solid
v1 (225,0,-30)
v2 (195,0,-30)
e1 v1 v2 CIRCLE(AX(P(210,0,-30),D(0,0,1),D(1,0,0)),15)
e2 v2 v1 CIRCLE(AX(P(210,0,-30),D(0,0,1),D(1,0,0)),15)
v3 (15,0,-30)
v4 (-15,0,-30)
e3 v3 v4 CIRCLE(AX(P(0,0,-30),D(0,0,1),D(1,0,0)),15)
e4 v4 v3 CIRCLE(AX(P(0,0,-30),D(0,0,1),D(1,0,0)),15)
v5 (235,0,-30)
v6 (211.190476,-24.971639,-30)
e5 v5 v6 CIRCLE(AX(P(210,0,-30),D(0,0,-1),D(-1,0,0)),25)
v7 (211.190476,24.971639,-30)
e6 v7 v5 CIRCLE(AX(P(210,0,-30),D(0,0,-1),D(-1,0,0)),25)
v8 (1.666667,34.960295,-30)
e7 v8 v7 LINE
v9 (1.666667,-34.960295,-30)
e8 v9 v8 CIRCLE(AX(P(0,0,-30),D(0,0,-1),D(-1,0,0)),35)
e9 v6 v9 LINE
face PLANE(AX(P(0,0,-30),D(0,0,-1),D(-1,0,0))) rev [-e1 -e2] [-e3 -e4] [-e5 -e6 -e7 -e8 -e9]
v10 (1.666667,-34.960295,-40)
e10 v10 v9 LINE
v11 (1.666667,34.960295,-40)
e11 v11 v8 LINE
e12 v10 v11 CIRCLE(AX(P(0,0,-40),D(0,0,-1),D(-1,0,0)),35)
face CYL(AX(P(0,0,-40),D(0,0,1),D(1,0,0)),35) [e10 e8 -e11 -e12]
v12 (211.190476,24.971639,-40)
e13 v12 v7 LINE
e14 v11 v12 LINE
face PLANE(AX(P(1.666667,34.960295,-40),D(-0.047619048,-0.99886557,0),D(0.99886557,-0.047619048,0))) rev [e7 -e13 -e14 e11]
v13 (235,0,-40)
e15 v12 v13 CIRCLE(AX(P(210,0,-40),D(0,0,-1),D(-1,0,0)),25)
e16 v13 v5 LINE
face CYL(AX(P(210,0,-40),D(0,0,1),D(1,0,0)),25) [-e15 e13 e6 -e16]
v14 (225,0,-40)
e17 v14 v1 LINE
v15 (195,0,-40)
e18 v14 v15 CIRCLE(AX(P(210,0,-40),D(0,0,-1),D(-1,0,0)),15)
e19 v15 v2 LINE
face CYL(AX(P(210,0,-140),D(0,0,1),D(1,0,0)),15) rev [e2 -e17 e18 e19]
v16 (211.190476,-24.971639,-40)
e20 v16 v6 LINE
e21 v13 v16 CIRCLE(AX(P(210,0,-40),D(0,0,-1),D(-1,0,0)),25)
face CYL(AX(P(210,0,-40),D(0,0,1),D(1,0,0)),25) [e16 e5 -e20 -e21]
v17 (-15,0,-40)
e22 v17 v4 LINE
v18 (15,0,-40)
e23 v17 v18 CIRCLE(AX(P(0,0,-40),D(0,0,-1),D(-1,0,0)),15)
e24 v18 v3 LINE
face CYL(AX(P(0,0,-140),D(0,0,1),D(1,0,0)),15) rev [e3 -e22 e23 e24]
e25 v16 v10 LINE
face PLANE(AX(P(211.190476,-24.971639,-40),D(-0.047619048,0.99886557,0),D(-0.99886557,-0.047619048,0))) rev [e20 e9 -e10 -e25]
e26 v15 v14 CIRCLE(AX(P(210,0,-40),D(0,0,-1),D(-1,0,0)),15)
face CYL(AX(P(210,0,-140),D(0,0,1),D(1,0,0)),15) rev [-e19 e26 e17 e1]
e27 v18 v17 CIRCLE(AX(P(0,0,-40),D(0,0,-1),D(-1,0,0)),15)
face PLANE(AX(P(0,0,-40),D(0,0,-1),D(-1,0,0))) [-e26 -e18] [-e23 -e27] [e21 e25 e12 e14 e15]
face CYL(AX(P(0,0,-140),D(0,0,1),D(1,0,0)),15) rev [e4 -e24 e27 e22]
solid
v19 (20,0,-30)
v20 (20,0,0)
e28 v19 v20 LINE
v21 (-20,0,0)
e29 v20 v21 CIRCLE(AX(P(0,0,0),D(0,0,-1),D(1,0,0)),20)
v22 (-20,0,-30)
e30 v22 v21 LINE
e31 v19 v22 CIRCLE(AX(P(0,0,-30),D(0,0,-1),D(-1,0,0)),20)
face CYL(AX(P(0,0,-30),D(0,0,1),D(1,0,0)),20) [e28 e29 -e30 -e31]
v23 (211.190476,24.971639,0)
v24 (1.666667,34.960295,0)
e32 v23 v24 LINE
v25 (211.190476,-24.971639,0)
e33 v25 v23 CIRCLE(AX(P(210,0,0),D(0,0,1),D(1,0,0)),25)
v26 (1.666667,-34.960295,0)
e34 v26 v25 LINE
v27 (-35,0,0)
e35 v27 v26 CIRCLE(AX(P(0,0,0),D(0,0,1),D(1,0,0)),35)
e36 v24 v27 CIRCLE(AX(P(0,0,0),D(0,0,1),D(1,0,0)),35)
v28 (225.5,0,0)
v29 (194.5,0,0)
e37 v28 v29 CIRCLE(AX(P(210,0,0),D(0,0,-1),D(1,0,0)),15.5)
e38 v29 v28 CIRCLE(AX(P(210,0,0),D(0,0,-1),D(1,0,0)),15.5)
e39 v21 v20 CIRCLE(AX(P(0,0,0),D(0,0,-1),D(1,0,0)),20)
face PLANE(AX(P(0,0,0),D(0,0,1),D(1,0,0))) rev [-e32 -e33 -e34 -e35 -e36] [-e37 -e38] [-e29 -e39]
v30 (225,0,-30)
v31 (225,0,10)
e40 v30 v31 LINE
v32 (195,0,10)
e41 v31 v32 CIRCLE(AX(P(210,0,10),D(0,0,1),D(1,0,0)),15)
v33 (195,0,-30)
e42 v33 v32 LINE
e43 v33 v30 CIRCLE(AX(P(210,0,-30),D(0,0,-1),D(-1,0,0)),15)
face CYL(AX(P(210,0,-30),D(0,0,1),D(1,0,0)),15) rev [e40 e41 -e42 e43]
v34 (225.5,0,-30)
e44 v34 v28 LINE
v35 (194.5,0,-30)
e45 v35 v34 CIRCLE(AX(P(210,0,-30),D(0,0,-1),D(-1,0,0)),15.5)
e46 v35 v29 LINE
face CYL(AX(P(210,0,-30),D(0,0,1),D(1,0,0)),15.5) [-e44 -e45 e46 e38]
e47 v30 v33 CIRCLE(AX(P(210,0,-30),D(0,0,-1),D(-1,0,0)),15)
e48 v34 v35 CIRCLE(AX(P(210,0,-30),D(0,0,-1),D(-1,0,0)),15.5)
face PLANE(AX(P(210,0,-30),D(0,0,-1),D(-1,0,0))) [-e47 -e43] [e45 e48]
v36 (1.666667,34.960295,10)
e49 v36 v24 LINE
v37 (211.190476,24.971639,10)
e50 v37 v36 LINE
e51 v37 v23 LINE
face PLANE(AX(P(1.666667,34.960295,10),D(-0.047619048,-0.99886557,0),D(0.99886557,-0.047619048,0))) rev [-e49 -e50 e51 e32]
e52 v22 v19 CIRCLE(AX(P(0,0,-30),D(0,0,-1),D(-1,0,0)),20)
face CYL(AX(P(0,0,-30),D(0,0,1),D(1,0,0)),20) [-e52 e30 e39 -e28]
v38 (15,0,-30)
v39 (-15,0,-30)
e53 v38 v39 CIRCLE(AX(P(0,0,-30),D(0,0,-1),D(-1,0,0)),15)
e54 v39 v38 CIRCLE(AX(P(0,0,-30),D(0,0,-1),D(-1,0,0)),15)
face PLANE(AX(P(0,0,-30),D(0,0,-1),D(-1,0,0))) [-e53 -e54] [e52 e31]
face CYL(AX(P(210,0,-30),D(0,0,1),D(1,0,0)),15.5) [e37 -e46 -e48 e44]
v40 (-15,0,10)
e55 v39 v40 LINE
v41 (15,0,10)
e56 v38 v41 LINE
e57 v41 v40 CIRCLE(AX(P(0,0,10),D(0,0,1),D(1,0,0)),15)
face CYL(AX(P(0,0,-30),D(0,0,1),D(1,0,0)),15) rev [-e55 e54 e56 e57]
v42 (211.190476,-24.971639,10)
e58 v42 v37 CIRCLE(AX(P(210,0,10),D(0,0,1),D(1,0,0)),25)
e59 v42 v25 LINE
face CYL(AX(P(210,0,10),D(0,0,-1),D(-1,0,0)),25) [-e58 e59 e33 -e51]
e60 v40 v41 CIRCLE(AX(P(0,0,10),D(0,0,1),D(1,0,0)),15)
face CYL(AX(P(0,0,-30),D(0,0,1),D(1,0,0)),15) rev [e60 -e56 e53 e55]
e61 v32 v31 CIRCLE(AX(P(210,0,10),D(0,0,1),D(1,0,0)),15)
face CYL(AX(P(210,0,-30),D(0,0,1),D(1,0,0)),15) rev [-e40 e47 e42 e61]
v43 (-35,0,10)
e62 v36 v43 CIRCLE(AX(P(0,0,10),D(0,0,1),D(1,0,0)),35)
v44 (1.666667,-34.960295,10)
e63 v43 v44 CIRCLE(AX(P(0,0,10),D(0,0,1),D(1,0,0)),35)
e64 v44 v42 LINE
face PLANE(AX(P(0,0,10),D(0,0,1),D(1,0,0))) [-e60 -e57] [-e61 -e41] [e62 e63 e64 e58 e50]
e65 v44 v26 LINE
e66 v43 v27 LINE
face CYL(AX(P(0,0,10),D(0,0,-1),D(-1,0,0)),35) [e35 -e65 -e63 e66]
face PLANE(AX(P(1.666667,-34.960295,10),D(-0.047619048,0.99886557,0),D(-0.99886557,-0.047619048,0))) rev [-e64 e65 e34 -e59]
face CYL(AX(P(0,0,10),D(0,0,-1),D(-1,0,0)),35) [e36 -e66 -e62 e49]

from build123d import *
from build123d.topology import SkipClean

# Parameters (mm, degrees)
BOSS_EXTRUDE1_DEPTH = 10
SKETCH3_R           = 20
SKETCH3_R_2         = 15
SKETCH3_R_3         = 15.5
BOSS_EXTRUDE2_DEPTH = 30
CUT_EXTRUDE1_START  = -106
SKETCH5_R           = 15
CUT_EXTRUDE1_DEPTH  = 106
BOSS_EXTRUDE3_START = 30
BOSS_EXTRUDE3_DEPTH = 10
SKETCH7_R           = 15
CUT_EXTRUDE2_DEPTH  = 110


with BuildPart() as part:
    # Sketch1 → Boss-Extrude1 (new body)
    with BuildSketch(Plane.XY):
        with BuildLine():
            Line((1.666666667, 34.960294939), (211.19047619, 24.971639242))
            ThreePointArc((211.19047619, 24.971639242), (235, 0), (211.19047619, -24.971639242))
            Line((211.19047619, -24.971639242), (1.666666667, -34.960294939))
            ThreePointArc((1.666666667, -34.960294939), (-35, 0), (1.666666667, 34.960294939))
        make_face()
    extrude(amount=BOSS_EXTRUDE1_DEPTH)

    # Sketch3 → Boss-Extrude2 (add)
    # profile 1 of 2: a face of its own
    with BuildSketch(Plane(origin=(0, 0, 0), x_dir=(-1, 0, 0), z_dir=(0, 0, -1))):
        with Locations(Location((0, 0, 0), (0, 0, 180))):
            Circle(SKETCH3_R)
        Circle(SKETCH3_R_2, mode=Mode.SUBTRACT)
    # profile 2 of 2: a face of its own
    with BuildSketch(Plane(origin=(0, 0, 0), x_dir=(-1, 0, 0), z_dir=(0, 0, -1))):
        with Locations(Location((-210, 0, 0), (0, 0, 180))):
            Circle(SKETCH3_R_3)
        with Locations((-210, 0)):
            Circle(SKETCH3_R_2, mode=Mode.SUBTRACT)
    extrude(amount=BOSS_EXTRUDE2_DEPTH)

    # Sketch5 → Cut-Extrude1 (cut)
    with SkipClean():  # the faces are left unmerged after this step: merging them gives an invalid solid
        with BuildSketch(Plane(origin=(0, 0, -30), x_dir=(-1, 0, 0), z_dir=(0, 0, -1)).offset(CUT_EXTRUDE1_START)):
            with Locations(Location((0, 0, 0), (0, 0, 180))):
                Circle(SKETCH5_R)
            with Locations(Location((-210, 0, 0), (0, 0, 180))):
                Circle(SKETCH5_R)
        extrude(amount=CUT_EXTRUDE1_DEPTH, mode=Mode.SUBTRACT)


with BuildPart() as body_2:
    # Sketch6 → Boss-Extrude3 (new body)
    with BuildSketch(Plane(origin=(0, 0, 0), x_dir=(-1, 0, 0), z_dir=(0, 0, -1)).offset(BOSS_EXTRUDE3_START)):
        with BuildLine():
            Line((-1.666666667, 34.960294939), (-211.19047619, 24.971639242))
            ThreePointArc((-211.19047619, 24.971639242), (-235, 0), (-211.19047619, -24.971639242))
            Line((-211.19047619, -24.971639242), (-1.666666667, -34.960294939))
            ThreePointArc((-1.666666667, -34.960294939), (35, 0), (-1.666666667, 34.960294939))
        make_face()
    extrude(amount=BOSS_EXTRUDE3_DEPTH)

    # Sketch7 → Cut-Extrude2 (cut)
    with BuildSketch(Plane.XY.offset(-30)):
        with Locations((210, 0)):
            Circle(SKETCH7_R)
        Circle(SKETCH7_R)
    extrude(amount=-CUT_EXTRUDE2_DEPTH, mode=Mode.SUBTRACT)


solid = Compound([part.part, body_2.part])
